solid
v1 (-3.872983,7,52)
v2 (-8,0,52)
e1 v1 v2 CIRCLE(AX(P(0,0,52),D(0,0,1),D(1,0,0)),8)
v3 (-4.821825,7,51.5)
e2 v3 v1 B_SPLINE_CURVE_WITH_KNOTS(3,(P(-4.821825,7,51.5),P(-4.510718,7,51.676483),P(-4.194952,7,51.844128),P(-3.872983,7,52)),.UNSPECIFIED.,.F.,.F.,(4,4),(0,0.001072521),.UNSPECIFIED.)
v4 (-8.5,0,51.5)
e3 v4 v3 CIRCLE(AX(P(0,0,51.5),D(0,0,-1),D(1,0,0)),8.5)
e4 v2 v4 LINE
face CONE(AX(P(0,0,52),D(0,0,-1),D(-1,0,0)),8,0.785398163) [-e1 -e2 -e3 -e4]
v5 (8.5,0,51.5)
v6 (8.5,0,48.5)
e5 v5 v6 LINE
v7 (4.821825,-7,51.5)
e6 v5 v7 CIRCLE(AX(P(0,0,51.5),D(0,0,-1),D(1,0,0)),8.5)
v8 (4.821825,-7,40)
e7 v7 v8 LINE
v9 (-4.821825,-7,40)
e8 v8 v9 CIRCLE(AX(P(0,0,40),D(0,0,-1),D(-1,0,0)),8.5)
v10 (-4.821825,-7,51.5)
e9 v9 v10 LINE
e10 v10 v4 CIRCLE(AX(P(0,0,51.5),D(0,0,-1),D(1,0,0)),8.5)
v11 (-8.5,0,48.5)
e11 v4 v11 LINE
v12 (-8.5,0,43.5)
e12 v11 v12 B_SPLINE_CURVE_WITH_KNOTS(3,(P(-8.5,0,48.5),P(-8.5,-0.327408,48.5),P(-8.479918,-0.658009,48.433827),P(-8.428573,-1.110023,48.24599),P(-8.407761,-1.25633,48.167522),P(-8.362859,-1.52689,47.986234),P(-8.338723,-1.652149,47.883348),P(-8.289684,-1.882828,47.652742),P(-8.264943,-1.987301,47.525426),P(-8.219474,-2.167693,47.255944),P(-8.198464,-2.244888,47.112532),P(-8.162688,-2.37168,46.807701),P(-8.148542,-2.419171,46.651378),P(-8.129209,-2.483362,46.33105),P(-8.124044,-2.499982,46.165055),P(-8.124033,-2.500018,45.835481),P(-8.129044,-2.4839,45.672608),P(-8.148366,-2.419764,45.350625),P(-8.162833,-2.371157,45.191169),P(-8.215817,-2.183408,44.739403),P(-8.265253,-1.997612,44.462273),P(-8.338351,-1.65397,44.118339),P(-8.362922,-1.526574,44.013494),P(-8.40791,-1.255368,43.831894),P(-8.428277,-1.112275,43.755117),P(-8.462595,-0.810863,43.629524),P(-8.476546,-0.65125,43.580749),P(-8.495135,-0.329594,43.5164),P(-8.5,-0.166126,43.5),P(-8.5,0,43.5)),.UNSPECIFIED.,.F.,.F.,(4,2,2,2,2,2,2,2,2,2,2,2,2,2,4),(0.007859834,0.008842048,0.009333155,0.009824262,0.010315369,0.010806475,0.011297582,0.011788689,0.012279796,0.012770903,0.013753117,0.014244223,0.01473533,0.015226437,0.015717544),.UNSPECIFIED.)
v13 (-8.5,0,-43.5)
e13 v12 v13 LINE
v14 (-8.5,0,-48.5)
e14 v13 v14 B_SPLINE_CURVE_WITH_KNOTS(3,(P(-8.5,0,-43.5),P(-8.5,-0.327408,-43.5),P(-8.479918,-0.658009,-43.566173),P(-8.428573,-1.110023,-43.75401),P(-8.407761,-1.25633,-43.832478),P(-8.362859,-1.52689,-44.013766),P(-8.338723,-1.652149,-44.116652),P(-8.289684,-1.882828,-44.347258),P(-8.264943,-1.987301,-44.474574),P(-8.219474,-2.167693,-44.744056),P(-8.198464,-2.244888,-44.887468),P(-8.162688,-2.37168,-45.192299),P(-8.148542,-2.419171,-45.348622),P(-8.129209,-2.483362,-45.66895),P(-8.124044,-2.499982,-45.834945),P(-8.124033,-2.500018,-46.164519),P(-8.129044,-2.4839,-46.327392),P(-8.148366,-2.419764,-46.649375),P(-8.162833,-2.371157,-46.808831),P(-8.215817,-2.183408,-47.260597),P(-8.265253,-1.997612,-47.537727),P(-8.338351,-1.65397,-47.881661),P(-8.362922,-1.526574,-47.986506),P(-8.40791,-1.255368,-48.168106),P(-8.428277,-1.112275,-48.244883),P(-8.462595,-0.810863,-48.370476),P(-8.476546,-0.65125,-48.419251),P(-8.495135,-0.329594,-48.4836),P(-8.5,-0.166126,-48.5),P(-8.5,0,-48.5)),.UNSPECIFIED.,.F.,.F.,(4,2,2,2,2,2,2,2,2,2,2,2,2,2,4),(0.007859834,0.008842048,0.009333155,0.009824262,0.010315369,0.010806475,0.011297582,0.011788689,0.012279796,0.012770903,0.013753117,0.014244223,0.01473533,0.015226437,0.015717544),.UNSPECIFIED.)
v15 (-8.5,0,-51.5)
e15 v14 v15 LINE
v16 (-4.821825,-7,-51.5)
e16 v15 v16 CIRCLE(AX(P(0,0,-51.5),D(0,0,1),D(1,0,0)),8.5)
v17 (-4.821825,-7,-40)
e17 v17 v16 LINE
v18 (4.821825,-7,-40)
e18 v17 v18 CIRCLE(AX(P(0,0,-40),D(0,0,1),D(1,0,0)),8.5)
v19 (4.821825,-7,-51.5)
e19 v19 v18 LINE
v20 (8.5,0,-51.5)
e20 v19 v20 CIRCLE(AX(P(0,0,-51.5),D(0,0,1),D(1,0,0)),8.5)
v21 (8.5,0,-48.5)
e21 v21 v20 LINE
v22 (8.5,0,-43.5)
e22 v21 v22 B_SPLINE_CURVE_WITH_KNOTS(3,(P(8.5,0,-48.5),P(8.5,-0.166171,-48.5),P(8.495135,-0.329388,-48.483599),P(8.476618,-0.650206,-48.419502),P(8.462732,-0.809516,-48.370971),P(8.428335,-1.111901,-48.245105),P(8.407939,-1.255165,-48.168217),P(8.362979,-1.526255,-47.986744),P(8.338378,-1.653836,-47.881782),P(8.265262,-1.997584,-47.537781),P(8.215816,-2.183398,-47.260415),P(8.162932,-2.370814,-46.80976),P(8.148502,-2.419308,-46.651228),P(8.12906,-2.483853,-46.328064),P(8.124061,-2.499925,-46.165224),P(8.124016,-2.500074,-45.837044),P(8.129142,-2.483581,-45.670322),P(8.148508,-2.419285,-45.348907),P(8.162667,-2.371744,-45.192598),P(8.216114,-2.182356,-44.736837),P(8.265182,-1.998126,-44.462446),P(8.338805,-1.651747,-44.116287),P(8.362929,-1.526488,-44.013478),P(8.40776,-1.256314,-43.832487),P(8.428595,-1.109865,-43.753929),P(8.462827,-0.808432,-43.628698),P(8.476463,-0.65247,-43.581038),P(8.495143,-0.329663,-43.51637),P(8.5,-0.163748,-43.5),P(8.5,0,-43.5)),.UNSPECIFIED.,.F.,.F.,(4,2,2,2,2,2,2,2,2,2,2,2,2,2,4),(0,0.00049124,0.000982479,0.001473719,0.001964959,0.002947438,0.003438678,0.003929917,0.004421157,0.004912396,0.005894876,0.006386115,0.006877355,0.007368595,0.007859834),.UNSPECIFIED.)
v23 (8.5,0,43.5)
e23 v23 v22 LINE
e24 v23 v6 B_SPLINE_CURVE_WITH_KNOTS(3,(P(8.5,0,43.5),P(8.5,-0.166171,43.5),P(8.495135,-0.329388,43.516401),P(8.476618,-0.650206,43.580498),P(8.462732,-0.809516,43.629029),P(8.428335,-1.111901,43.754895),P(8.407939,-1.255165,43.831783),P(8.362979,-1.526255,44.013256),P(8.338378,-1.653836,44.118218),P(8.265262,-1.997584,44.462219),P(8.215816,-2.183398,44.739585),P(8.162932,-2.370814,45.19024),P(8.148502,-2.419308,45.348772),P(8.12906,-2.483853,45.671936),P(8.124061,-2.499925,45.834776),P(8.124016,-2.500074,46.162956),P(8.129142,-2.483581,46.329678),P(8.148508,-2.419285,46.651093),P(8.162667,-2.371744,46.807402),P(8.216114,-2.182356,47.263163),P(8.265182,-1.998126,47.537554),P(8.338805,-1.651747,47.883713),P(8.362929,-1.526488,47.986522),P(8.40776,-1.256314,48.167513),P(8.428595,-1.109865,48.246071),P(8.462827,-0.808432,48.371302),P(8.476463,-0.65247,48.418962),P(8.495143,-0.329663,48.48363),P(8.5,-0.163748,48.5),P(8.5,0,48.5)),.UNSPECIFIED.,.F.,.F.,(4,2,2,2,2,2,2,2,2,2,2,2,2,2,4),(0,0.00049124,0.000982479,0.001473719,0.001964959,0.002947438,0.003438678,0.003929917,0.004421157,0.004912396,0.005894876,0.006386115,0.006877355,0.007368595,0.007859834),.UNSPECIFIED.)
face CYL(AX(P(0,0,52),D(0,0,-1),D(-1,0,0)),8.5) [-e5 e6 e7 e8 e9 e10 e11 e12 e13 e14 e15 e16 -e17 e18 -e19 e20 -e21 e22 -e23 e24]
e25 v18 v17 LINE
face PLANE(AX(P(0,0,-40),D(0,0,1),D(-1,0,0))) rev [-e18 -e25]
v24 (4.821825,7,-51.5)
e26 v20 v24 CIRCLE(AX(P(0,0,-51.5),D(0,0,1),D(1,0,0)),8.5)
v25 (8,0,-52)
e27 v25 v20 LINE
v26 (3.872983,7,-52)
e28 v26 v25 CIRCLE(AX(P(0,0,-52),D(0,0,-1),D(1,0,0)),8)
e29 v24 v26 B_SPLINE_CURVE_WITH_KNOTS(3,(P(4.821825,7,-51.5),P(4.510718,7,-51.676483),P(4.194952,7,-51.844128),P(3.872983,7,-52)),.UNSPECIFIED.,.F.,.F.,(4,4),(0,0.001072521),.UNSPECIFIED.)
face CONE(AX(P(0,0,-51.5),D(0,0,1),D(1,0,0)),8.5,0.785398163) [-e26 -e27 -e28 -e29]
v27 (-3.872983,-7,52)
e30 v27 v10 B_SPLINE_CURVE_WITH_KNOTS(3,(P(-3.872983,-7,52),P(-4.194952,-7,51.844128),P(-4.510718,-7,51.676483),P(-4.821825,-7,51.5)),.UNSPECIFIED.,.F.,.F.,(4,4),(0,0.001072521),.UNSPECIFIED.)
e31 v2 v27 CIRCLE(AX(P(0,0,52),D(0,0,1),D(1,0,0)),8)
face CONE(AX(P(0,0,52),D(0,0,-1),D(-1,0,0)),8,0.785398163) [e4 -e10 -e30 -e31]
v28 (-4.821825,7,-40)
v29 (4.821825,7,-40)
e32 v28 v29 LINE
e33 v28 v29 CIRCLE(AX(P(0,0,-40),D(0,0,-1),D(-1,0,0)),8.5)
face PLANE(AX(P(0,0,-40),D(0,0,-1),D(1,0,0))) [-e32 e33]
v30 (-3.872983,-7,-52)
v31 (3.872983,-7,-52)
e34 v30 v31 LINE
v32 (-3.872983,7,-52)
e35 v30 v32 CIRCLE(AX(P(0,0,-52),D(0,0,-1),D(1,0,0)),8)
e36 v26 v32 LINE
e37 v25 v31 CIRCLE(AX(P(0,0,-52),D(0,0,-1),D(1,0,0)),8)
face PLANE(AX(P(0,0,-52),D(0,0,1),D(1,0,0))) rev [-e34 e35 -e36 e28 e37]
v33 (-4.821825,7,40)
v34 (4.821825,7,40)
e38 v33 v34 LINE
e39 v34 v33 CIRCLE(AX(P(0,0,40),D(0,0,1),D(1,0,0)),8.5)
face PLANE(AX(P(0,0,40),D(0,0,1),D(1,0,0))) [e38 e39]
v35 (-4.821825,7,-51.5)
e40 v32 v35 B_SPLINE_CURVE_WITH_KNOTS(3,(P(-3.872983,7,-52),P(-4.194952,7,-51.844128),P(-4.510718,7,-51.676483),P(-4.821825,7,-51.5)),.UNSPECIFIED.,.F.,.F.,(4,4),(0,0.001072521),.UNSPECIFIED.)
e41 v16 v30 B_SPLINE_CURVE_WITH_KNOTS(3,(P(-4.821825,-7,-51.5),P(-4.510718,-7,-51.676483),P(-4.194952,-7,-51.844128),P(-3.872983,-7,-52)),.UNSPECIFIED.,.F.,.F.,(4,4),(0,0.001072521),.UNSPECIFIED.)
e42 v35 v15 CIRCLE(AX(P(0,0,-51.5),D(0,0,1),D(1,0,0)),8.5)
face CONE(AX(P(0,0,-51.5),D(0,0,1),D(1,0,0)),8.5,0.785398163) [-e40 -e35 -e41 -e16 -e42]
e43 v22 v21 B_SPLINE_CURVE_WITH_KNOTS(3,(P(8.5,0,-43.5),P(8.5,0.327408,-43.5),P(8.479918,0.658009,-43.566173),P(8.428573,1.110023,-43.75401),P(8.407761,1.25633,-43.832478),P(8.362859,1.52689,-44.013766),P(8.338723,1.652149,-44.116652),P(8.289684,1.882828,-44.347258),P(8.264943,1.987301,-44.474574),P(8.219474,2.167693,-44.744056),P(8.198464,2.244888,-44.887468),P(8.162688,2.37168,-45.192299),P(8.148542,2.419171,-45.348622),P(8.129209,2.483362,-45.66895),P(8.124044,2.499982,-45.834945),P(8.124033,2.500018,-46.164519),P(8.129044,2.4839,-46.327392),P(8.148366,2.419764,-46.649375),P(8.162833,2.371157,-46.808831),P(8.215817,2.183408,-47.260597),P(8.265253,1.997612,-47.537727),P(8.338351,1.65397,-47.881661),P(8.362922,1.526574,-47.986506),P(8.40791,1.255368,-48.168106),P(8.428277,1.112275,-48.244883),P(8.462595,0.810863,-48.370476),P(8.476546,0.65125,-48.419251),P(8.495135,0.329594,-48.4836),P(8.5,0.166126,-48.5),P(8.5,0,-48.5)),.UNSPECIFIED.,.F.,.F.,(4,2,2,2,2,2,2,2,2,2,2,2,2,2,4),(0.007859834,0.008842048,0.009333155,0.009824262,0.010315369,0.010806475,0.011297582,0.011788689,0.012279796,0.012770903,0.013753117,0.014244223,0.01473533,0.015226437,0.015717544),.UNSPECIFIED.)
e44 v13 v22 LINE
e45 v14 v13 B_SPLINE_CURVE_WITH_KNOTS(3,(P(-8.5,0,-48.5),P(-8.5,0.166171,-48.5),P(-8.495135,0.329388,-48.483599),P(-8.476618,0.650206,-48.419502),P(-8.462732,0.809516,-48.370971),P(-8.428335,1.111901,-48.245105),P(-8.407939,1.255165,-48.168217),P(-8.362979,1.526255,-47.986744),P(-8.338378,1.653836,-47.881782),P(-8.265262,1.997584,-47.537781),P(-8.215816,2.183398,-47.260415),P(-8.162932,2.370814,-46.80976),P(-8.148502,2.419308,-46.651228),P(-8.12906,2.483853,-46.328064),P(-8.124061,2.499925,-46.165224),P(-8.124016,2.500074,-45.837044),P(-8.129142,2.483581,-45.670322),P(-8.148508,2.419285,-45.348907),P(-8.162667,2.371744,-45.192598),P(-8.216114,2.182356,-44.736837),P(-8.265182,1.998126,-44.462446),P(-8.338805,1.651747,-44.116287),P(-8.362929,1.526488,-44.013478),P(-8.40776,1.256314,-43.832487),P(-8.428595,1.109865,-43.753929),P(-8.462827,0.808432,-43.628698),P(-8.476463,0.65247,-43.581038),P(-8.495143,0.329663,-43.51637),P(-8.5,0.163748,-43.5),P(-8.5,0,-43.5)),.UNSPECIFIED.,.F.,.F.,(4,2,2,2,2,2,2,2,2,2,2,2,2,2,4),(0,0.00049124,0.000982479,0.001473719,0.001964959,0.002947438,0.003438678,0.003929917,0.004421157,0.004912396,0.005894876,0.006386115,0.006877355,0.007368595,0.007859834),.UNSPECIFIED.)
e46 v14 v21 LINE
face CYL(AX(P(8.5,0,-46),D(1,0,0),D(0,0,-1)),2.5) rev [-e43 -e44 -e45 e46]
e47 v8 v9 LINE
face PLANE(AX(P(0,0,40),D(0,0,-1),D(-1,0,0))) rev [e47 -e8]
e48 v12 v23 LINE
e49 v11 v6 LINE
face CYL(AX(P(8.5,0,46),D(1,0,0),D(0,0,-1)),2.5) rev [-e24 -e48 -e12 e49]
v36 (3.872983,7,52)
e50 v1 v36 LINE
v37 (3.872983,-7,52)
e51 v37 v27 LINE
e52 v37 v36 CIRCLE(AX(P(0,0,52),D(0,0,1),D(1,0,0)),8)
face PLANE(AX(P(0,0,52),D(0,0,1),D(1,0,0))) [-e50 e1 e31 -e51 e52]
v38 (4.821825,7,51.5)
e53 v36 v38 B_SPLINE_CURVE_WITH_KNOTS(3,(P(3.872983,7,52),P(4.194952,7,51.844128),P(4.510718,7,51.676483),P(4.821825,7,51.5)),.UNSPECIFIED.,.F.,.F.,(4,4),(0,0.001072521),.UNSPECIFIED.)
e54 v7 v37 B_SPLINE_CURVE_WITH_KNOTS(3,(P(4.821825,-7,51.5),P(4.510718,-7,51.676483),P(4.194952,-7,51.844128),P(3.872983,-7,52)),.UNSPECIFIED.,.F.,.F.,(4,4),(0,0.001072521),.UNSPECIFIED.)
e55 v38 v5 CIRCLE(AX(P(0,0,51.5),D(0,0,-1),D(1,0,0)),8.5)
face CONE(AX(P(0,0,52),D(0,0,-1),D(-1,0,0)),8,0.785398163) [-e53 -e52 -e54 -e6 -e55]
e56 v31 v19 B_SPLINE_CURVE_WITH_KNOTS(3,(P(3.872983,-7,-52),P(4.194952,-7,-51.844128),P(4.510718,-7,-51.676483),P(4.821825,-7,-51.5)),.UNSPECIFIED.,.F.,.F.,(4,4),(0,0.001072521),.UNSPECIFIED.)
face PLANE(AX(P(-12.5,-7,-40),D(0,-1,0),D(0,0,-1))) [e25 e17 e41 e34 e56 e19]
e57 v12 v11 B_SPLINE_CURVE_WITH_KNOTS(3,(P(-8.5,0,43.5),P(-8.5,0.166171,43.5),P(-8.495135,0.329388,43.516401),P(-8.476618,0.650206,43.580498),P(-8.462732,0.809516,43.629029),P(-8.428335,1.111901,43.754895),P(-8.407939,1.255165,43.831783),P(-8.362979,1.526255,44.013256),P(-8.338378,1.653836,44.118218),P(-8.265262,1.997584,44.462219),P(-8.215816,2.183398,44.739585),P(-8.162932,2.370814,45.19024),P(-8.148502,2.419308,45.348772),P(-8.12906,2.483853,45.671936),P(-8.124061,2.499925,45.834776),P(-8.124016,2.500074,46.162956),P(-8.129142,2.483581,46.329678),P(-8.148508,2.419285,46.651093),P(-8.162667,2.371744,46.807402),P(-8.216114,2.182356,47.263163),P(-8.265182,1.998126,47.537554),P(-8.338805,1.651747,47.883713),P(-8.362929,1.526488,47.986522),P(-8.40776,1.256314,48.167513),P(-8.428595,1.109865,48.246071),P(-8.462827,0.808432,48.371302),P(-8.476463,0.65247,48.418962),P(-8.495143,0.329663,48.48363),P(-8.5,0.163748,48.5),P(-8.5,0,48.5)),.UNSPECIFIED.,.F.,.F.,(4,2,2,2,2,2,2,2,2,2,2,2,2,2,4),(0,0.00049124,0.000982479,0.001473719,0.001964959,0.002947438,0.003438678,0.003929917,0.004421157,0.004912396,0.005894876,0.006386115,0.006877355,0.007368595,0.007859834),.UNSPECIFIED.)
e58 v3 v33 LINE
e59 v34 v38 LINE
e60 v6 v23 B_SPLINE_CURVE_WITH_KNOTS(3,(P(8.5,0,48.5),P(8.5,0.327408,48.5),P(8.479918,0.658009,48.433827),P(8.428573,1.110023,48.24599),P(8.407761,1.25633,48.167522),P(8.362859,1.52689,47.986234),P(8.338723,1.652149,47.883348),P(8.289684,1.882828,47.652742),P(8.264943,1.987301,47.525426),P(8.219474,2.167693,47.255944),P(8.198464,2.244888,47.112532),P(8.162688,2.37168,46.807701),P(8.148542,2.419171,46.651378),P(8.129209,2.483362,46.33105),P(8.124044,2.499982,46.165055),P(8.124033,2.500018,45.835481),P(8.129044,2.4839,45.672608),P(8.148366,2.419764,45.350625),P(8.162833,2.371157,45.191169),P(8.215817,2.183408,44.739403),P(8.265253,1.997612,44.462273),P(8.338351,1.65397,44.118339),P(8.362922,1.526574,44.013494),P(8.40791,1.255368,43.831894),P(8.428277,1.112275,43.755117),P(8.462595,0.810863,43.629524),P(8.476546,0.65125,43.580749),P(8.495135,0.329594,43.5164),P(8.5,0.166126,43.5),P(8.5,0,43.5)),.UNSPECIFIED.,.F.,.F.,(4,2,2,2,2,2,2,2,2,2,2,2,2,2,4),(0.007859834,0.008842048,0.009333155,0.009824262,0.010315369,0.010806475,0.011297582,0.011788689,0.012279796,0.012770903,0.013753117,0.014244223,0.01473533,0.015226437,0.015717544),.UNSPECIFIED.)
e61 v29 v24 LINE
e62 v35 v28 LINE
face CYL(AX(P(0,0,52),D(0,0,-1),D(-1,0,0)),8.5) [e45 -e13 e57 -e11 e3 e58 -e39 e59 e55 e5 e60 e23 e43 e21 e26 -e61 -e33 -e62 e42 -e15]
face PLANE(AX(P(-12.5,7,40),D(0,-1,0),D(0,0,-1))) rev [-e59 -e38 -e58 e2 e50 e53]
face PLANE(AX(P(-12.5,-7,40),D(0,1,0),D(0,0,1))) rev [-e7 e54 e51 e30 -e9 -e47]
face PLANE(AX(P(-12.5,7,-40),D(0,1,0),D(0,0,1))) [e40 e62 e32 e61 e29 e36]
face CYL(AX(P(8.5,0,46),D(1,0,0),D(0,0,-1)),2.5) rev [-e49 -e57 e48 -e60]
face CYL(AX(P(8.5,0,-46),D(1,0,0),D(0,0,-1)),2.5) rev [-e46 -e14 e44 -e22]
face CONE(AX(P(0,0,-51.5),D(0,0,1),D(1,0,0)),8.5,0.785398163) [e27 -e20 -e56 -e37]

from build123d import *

# Parameters (mm, degrees)
SKETCH_1_R          = 8.5
EXTRUDE_1_DEPTH     = 52
SKETCH_2_W          = 25
SKETCH_2_H          = 3
CUT_EXTRUDE_1_DEPTH = 12
CHAMFER_2_SIZE      = 0.5
HOLE_WIZARD_M6_1_D  = 5


with BuildPart() as part:
    # 草图1 → 凸台-拉伸1 (new, symmetric)
    with BuildSketch(Plane.XY):
        with Locations(Location((0, 0, 0), (0, 0, 180))):
            Circle(SKETCH_1_R)
    extrude(amount=EXTRUDE_1_DEPTH, both=True)

    # 草图2 → 切除-拉伸1 (cut)
    with BuildSketch(Plane.XY.offset(52)):
        with Locations((0, 8.5)):
            Rectangle(SKETCH_2_W, SKETCH_2_H)
        with Locations((0, -8.5)):
            Rectangle(SKETCH_2_W, SKETCH_2_H)
    cut_extrude_1 = extrude(amount=-CUT_EXTRUDE_1_DEPTH, mode=Mode.SUBTRACT)

    # 镜向1: 切除-拉伸1 across plane
    add(cut_extrude_1.mirror(Plane.XY), mode=Mode.SUBTRACT)

    # 倒角2
    chamfer_2_edges = [part.edges().sort_by_distance(p)[0] for p in [
        (8.5, 0, 52),
        (-7.524477249, 3.953763034, -52),
        (8.5, 0, -52),
        (-7.524477249, 3.953763034, 52),
    ]]
    chamfer(chamfer_2_edges, length=CHAMFER_2_SIZE)

    # M6 螺纹孔1 (through all)
    with Locations(Plane(origin=(8.5, 0, 0), x_dir=(0, 0, -1), z_dir=(1, 0, 0))):
        with Locations((-46, 0), (46, 0)):
            Hole(HOLE_WIZARD_M6_1_D / 2)


solid = part.part
